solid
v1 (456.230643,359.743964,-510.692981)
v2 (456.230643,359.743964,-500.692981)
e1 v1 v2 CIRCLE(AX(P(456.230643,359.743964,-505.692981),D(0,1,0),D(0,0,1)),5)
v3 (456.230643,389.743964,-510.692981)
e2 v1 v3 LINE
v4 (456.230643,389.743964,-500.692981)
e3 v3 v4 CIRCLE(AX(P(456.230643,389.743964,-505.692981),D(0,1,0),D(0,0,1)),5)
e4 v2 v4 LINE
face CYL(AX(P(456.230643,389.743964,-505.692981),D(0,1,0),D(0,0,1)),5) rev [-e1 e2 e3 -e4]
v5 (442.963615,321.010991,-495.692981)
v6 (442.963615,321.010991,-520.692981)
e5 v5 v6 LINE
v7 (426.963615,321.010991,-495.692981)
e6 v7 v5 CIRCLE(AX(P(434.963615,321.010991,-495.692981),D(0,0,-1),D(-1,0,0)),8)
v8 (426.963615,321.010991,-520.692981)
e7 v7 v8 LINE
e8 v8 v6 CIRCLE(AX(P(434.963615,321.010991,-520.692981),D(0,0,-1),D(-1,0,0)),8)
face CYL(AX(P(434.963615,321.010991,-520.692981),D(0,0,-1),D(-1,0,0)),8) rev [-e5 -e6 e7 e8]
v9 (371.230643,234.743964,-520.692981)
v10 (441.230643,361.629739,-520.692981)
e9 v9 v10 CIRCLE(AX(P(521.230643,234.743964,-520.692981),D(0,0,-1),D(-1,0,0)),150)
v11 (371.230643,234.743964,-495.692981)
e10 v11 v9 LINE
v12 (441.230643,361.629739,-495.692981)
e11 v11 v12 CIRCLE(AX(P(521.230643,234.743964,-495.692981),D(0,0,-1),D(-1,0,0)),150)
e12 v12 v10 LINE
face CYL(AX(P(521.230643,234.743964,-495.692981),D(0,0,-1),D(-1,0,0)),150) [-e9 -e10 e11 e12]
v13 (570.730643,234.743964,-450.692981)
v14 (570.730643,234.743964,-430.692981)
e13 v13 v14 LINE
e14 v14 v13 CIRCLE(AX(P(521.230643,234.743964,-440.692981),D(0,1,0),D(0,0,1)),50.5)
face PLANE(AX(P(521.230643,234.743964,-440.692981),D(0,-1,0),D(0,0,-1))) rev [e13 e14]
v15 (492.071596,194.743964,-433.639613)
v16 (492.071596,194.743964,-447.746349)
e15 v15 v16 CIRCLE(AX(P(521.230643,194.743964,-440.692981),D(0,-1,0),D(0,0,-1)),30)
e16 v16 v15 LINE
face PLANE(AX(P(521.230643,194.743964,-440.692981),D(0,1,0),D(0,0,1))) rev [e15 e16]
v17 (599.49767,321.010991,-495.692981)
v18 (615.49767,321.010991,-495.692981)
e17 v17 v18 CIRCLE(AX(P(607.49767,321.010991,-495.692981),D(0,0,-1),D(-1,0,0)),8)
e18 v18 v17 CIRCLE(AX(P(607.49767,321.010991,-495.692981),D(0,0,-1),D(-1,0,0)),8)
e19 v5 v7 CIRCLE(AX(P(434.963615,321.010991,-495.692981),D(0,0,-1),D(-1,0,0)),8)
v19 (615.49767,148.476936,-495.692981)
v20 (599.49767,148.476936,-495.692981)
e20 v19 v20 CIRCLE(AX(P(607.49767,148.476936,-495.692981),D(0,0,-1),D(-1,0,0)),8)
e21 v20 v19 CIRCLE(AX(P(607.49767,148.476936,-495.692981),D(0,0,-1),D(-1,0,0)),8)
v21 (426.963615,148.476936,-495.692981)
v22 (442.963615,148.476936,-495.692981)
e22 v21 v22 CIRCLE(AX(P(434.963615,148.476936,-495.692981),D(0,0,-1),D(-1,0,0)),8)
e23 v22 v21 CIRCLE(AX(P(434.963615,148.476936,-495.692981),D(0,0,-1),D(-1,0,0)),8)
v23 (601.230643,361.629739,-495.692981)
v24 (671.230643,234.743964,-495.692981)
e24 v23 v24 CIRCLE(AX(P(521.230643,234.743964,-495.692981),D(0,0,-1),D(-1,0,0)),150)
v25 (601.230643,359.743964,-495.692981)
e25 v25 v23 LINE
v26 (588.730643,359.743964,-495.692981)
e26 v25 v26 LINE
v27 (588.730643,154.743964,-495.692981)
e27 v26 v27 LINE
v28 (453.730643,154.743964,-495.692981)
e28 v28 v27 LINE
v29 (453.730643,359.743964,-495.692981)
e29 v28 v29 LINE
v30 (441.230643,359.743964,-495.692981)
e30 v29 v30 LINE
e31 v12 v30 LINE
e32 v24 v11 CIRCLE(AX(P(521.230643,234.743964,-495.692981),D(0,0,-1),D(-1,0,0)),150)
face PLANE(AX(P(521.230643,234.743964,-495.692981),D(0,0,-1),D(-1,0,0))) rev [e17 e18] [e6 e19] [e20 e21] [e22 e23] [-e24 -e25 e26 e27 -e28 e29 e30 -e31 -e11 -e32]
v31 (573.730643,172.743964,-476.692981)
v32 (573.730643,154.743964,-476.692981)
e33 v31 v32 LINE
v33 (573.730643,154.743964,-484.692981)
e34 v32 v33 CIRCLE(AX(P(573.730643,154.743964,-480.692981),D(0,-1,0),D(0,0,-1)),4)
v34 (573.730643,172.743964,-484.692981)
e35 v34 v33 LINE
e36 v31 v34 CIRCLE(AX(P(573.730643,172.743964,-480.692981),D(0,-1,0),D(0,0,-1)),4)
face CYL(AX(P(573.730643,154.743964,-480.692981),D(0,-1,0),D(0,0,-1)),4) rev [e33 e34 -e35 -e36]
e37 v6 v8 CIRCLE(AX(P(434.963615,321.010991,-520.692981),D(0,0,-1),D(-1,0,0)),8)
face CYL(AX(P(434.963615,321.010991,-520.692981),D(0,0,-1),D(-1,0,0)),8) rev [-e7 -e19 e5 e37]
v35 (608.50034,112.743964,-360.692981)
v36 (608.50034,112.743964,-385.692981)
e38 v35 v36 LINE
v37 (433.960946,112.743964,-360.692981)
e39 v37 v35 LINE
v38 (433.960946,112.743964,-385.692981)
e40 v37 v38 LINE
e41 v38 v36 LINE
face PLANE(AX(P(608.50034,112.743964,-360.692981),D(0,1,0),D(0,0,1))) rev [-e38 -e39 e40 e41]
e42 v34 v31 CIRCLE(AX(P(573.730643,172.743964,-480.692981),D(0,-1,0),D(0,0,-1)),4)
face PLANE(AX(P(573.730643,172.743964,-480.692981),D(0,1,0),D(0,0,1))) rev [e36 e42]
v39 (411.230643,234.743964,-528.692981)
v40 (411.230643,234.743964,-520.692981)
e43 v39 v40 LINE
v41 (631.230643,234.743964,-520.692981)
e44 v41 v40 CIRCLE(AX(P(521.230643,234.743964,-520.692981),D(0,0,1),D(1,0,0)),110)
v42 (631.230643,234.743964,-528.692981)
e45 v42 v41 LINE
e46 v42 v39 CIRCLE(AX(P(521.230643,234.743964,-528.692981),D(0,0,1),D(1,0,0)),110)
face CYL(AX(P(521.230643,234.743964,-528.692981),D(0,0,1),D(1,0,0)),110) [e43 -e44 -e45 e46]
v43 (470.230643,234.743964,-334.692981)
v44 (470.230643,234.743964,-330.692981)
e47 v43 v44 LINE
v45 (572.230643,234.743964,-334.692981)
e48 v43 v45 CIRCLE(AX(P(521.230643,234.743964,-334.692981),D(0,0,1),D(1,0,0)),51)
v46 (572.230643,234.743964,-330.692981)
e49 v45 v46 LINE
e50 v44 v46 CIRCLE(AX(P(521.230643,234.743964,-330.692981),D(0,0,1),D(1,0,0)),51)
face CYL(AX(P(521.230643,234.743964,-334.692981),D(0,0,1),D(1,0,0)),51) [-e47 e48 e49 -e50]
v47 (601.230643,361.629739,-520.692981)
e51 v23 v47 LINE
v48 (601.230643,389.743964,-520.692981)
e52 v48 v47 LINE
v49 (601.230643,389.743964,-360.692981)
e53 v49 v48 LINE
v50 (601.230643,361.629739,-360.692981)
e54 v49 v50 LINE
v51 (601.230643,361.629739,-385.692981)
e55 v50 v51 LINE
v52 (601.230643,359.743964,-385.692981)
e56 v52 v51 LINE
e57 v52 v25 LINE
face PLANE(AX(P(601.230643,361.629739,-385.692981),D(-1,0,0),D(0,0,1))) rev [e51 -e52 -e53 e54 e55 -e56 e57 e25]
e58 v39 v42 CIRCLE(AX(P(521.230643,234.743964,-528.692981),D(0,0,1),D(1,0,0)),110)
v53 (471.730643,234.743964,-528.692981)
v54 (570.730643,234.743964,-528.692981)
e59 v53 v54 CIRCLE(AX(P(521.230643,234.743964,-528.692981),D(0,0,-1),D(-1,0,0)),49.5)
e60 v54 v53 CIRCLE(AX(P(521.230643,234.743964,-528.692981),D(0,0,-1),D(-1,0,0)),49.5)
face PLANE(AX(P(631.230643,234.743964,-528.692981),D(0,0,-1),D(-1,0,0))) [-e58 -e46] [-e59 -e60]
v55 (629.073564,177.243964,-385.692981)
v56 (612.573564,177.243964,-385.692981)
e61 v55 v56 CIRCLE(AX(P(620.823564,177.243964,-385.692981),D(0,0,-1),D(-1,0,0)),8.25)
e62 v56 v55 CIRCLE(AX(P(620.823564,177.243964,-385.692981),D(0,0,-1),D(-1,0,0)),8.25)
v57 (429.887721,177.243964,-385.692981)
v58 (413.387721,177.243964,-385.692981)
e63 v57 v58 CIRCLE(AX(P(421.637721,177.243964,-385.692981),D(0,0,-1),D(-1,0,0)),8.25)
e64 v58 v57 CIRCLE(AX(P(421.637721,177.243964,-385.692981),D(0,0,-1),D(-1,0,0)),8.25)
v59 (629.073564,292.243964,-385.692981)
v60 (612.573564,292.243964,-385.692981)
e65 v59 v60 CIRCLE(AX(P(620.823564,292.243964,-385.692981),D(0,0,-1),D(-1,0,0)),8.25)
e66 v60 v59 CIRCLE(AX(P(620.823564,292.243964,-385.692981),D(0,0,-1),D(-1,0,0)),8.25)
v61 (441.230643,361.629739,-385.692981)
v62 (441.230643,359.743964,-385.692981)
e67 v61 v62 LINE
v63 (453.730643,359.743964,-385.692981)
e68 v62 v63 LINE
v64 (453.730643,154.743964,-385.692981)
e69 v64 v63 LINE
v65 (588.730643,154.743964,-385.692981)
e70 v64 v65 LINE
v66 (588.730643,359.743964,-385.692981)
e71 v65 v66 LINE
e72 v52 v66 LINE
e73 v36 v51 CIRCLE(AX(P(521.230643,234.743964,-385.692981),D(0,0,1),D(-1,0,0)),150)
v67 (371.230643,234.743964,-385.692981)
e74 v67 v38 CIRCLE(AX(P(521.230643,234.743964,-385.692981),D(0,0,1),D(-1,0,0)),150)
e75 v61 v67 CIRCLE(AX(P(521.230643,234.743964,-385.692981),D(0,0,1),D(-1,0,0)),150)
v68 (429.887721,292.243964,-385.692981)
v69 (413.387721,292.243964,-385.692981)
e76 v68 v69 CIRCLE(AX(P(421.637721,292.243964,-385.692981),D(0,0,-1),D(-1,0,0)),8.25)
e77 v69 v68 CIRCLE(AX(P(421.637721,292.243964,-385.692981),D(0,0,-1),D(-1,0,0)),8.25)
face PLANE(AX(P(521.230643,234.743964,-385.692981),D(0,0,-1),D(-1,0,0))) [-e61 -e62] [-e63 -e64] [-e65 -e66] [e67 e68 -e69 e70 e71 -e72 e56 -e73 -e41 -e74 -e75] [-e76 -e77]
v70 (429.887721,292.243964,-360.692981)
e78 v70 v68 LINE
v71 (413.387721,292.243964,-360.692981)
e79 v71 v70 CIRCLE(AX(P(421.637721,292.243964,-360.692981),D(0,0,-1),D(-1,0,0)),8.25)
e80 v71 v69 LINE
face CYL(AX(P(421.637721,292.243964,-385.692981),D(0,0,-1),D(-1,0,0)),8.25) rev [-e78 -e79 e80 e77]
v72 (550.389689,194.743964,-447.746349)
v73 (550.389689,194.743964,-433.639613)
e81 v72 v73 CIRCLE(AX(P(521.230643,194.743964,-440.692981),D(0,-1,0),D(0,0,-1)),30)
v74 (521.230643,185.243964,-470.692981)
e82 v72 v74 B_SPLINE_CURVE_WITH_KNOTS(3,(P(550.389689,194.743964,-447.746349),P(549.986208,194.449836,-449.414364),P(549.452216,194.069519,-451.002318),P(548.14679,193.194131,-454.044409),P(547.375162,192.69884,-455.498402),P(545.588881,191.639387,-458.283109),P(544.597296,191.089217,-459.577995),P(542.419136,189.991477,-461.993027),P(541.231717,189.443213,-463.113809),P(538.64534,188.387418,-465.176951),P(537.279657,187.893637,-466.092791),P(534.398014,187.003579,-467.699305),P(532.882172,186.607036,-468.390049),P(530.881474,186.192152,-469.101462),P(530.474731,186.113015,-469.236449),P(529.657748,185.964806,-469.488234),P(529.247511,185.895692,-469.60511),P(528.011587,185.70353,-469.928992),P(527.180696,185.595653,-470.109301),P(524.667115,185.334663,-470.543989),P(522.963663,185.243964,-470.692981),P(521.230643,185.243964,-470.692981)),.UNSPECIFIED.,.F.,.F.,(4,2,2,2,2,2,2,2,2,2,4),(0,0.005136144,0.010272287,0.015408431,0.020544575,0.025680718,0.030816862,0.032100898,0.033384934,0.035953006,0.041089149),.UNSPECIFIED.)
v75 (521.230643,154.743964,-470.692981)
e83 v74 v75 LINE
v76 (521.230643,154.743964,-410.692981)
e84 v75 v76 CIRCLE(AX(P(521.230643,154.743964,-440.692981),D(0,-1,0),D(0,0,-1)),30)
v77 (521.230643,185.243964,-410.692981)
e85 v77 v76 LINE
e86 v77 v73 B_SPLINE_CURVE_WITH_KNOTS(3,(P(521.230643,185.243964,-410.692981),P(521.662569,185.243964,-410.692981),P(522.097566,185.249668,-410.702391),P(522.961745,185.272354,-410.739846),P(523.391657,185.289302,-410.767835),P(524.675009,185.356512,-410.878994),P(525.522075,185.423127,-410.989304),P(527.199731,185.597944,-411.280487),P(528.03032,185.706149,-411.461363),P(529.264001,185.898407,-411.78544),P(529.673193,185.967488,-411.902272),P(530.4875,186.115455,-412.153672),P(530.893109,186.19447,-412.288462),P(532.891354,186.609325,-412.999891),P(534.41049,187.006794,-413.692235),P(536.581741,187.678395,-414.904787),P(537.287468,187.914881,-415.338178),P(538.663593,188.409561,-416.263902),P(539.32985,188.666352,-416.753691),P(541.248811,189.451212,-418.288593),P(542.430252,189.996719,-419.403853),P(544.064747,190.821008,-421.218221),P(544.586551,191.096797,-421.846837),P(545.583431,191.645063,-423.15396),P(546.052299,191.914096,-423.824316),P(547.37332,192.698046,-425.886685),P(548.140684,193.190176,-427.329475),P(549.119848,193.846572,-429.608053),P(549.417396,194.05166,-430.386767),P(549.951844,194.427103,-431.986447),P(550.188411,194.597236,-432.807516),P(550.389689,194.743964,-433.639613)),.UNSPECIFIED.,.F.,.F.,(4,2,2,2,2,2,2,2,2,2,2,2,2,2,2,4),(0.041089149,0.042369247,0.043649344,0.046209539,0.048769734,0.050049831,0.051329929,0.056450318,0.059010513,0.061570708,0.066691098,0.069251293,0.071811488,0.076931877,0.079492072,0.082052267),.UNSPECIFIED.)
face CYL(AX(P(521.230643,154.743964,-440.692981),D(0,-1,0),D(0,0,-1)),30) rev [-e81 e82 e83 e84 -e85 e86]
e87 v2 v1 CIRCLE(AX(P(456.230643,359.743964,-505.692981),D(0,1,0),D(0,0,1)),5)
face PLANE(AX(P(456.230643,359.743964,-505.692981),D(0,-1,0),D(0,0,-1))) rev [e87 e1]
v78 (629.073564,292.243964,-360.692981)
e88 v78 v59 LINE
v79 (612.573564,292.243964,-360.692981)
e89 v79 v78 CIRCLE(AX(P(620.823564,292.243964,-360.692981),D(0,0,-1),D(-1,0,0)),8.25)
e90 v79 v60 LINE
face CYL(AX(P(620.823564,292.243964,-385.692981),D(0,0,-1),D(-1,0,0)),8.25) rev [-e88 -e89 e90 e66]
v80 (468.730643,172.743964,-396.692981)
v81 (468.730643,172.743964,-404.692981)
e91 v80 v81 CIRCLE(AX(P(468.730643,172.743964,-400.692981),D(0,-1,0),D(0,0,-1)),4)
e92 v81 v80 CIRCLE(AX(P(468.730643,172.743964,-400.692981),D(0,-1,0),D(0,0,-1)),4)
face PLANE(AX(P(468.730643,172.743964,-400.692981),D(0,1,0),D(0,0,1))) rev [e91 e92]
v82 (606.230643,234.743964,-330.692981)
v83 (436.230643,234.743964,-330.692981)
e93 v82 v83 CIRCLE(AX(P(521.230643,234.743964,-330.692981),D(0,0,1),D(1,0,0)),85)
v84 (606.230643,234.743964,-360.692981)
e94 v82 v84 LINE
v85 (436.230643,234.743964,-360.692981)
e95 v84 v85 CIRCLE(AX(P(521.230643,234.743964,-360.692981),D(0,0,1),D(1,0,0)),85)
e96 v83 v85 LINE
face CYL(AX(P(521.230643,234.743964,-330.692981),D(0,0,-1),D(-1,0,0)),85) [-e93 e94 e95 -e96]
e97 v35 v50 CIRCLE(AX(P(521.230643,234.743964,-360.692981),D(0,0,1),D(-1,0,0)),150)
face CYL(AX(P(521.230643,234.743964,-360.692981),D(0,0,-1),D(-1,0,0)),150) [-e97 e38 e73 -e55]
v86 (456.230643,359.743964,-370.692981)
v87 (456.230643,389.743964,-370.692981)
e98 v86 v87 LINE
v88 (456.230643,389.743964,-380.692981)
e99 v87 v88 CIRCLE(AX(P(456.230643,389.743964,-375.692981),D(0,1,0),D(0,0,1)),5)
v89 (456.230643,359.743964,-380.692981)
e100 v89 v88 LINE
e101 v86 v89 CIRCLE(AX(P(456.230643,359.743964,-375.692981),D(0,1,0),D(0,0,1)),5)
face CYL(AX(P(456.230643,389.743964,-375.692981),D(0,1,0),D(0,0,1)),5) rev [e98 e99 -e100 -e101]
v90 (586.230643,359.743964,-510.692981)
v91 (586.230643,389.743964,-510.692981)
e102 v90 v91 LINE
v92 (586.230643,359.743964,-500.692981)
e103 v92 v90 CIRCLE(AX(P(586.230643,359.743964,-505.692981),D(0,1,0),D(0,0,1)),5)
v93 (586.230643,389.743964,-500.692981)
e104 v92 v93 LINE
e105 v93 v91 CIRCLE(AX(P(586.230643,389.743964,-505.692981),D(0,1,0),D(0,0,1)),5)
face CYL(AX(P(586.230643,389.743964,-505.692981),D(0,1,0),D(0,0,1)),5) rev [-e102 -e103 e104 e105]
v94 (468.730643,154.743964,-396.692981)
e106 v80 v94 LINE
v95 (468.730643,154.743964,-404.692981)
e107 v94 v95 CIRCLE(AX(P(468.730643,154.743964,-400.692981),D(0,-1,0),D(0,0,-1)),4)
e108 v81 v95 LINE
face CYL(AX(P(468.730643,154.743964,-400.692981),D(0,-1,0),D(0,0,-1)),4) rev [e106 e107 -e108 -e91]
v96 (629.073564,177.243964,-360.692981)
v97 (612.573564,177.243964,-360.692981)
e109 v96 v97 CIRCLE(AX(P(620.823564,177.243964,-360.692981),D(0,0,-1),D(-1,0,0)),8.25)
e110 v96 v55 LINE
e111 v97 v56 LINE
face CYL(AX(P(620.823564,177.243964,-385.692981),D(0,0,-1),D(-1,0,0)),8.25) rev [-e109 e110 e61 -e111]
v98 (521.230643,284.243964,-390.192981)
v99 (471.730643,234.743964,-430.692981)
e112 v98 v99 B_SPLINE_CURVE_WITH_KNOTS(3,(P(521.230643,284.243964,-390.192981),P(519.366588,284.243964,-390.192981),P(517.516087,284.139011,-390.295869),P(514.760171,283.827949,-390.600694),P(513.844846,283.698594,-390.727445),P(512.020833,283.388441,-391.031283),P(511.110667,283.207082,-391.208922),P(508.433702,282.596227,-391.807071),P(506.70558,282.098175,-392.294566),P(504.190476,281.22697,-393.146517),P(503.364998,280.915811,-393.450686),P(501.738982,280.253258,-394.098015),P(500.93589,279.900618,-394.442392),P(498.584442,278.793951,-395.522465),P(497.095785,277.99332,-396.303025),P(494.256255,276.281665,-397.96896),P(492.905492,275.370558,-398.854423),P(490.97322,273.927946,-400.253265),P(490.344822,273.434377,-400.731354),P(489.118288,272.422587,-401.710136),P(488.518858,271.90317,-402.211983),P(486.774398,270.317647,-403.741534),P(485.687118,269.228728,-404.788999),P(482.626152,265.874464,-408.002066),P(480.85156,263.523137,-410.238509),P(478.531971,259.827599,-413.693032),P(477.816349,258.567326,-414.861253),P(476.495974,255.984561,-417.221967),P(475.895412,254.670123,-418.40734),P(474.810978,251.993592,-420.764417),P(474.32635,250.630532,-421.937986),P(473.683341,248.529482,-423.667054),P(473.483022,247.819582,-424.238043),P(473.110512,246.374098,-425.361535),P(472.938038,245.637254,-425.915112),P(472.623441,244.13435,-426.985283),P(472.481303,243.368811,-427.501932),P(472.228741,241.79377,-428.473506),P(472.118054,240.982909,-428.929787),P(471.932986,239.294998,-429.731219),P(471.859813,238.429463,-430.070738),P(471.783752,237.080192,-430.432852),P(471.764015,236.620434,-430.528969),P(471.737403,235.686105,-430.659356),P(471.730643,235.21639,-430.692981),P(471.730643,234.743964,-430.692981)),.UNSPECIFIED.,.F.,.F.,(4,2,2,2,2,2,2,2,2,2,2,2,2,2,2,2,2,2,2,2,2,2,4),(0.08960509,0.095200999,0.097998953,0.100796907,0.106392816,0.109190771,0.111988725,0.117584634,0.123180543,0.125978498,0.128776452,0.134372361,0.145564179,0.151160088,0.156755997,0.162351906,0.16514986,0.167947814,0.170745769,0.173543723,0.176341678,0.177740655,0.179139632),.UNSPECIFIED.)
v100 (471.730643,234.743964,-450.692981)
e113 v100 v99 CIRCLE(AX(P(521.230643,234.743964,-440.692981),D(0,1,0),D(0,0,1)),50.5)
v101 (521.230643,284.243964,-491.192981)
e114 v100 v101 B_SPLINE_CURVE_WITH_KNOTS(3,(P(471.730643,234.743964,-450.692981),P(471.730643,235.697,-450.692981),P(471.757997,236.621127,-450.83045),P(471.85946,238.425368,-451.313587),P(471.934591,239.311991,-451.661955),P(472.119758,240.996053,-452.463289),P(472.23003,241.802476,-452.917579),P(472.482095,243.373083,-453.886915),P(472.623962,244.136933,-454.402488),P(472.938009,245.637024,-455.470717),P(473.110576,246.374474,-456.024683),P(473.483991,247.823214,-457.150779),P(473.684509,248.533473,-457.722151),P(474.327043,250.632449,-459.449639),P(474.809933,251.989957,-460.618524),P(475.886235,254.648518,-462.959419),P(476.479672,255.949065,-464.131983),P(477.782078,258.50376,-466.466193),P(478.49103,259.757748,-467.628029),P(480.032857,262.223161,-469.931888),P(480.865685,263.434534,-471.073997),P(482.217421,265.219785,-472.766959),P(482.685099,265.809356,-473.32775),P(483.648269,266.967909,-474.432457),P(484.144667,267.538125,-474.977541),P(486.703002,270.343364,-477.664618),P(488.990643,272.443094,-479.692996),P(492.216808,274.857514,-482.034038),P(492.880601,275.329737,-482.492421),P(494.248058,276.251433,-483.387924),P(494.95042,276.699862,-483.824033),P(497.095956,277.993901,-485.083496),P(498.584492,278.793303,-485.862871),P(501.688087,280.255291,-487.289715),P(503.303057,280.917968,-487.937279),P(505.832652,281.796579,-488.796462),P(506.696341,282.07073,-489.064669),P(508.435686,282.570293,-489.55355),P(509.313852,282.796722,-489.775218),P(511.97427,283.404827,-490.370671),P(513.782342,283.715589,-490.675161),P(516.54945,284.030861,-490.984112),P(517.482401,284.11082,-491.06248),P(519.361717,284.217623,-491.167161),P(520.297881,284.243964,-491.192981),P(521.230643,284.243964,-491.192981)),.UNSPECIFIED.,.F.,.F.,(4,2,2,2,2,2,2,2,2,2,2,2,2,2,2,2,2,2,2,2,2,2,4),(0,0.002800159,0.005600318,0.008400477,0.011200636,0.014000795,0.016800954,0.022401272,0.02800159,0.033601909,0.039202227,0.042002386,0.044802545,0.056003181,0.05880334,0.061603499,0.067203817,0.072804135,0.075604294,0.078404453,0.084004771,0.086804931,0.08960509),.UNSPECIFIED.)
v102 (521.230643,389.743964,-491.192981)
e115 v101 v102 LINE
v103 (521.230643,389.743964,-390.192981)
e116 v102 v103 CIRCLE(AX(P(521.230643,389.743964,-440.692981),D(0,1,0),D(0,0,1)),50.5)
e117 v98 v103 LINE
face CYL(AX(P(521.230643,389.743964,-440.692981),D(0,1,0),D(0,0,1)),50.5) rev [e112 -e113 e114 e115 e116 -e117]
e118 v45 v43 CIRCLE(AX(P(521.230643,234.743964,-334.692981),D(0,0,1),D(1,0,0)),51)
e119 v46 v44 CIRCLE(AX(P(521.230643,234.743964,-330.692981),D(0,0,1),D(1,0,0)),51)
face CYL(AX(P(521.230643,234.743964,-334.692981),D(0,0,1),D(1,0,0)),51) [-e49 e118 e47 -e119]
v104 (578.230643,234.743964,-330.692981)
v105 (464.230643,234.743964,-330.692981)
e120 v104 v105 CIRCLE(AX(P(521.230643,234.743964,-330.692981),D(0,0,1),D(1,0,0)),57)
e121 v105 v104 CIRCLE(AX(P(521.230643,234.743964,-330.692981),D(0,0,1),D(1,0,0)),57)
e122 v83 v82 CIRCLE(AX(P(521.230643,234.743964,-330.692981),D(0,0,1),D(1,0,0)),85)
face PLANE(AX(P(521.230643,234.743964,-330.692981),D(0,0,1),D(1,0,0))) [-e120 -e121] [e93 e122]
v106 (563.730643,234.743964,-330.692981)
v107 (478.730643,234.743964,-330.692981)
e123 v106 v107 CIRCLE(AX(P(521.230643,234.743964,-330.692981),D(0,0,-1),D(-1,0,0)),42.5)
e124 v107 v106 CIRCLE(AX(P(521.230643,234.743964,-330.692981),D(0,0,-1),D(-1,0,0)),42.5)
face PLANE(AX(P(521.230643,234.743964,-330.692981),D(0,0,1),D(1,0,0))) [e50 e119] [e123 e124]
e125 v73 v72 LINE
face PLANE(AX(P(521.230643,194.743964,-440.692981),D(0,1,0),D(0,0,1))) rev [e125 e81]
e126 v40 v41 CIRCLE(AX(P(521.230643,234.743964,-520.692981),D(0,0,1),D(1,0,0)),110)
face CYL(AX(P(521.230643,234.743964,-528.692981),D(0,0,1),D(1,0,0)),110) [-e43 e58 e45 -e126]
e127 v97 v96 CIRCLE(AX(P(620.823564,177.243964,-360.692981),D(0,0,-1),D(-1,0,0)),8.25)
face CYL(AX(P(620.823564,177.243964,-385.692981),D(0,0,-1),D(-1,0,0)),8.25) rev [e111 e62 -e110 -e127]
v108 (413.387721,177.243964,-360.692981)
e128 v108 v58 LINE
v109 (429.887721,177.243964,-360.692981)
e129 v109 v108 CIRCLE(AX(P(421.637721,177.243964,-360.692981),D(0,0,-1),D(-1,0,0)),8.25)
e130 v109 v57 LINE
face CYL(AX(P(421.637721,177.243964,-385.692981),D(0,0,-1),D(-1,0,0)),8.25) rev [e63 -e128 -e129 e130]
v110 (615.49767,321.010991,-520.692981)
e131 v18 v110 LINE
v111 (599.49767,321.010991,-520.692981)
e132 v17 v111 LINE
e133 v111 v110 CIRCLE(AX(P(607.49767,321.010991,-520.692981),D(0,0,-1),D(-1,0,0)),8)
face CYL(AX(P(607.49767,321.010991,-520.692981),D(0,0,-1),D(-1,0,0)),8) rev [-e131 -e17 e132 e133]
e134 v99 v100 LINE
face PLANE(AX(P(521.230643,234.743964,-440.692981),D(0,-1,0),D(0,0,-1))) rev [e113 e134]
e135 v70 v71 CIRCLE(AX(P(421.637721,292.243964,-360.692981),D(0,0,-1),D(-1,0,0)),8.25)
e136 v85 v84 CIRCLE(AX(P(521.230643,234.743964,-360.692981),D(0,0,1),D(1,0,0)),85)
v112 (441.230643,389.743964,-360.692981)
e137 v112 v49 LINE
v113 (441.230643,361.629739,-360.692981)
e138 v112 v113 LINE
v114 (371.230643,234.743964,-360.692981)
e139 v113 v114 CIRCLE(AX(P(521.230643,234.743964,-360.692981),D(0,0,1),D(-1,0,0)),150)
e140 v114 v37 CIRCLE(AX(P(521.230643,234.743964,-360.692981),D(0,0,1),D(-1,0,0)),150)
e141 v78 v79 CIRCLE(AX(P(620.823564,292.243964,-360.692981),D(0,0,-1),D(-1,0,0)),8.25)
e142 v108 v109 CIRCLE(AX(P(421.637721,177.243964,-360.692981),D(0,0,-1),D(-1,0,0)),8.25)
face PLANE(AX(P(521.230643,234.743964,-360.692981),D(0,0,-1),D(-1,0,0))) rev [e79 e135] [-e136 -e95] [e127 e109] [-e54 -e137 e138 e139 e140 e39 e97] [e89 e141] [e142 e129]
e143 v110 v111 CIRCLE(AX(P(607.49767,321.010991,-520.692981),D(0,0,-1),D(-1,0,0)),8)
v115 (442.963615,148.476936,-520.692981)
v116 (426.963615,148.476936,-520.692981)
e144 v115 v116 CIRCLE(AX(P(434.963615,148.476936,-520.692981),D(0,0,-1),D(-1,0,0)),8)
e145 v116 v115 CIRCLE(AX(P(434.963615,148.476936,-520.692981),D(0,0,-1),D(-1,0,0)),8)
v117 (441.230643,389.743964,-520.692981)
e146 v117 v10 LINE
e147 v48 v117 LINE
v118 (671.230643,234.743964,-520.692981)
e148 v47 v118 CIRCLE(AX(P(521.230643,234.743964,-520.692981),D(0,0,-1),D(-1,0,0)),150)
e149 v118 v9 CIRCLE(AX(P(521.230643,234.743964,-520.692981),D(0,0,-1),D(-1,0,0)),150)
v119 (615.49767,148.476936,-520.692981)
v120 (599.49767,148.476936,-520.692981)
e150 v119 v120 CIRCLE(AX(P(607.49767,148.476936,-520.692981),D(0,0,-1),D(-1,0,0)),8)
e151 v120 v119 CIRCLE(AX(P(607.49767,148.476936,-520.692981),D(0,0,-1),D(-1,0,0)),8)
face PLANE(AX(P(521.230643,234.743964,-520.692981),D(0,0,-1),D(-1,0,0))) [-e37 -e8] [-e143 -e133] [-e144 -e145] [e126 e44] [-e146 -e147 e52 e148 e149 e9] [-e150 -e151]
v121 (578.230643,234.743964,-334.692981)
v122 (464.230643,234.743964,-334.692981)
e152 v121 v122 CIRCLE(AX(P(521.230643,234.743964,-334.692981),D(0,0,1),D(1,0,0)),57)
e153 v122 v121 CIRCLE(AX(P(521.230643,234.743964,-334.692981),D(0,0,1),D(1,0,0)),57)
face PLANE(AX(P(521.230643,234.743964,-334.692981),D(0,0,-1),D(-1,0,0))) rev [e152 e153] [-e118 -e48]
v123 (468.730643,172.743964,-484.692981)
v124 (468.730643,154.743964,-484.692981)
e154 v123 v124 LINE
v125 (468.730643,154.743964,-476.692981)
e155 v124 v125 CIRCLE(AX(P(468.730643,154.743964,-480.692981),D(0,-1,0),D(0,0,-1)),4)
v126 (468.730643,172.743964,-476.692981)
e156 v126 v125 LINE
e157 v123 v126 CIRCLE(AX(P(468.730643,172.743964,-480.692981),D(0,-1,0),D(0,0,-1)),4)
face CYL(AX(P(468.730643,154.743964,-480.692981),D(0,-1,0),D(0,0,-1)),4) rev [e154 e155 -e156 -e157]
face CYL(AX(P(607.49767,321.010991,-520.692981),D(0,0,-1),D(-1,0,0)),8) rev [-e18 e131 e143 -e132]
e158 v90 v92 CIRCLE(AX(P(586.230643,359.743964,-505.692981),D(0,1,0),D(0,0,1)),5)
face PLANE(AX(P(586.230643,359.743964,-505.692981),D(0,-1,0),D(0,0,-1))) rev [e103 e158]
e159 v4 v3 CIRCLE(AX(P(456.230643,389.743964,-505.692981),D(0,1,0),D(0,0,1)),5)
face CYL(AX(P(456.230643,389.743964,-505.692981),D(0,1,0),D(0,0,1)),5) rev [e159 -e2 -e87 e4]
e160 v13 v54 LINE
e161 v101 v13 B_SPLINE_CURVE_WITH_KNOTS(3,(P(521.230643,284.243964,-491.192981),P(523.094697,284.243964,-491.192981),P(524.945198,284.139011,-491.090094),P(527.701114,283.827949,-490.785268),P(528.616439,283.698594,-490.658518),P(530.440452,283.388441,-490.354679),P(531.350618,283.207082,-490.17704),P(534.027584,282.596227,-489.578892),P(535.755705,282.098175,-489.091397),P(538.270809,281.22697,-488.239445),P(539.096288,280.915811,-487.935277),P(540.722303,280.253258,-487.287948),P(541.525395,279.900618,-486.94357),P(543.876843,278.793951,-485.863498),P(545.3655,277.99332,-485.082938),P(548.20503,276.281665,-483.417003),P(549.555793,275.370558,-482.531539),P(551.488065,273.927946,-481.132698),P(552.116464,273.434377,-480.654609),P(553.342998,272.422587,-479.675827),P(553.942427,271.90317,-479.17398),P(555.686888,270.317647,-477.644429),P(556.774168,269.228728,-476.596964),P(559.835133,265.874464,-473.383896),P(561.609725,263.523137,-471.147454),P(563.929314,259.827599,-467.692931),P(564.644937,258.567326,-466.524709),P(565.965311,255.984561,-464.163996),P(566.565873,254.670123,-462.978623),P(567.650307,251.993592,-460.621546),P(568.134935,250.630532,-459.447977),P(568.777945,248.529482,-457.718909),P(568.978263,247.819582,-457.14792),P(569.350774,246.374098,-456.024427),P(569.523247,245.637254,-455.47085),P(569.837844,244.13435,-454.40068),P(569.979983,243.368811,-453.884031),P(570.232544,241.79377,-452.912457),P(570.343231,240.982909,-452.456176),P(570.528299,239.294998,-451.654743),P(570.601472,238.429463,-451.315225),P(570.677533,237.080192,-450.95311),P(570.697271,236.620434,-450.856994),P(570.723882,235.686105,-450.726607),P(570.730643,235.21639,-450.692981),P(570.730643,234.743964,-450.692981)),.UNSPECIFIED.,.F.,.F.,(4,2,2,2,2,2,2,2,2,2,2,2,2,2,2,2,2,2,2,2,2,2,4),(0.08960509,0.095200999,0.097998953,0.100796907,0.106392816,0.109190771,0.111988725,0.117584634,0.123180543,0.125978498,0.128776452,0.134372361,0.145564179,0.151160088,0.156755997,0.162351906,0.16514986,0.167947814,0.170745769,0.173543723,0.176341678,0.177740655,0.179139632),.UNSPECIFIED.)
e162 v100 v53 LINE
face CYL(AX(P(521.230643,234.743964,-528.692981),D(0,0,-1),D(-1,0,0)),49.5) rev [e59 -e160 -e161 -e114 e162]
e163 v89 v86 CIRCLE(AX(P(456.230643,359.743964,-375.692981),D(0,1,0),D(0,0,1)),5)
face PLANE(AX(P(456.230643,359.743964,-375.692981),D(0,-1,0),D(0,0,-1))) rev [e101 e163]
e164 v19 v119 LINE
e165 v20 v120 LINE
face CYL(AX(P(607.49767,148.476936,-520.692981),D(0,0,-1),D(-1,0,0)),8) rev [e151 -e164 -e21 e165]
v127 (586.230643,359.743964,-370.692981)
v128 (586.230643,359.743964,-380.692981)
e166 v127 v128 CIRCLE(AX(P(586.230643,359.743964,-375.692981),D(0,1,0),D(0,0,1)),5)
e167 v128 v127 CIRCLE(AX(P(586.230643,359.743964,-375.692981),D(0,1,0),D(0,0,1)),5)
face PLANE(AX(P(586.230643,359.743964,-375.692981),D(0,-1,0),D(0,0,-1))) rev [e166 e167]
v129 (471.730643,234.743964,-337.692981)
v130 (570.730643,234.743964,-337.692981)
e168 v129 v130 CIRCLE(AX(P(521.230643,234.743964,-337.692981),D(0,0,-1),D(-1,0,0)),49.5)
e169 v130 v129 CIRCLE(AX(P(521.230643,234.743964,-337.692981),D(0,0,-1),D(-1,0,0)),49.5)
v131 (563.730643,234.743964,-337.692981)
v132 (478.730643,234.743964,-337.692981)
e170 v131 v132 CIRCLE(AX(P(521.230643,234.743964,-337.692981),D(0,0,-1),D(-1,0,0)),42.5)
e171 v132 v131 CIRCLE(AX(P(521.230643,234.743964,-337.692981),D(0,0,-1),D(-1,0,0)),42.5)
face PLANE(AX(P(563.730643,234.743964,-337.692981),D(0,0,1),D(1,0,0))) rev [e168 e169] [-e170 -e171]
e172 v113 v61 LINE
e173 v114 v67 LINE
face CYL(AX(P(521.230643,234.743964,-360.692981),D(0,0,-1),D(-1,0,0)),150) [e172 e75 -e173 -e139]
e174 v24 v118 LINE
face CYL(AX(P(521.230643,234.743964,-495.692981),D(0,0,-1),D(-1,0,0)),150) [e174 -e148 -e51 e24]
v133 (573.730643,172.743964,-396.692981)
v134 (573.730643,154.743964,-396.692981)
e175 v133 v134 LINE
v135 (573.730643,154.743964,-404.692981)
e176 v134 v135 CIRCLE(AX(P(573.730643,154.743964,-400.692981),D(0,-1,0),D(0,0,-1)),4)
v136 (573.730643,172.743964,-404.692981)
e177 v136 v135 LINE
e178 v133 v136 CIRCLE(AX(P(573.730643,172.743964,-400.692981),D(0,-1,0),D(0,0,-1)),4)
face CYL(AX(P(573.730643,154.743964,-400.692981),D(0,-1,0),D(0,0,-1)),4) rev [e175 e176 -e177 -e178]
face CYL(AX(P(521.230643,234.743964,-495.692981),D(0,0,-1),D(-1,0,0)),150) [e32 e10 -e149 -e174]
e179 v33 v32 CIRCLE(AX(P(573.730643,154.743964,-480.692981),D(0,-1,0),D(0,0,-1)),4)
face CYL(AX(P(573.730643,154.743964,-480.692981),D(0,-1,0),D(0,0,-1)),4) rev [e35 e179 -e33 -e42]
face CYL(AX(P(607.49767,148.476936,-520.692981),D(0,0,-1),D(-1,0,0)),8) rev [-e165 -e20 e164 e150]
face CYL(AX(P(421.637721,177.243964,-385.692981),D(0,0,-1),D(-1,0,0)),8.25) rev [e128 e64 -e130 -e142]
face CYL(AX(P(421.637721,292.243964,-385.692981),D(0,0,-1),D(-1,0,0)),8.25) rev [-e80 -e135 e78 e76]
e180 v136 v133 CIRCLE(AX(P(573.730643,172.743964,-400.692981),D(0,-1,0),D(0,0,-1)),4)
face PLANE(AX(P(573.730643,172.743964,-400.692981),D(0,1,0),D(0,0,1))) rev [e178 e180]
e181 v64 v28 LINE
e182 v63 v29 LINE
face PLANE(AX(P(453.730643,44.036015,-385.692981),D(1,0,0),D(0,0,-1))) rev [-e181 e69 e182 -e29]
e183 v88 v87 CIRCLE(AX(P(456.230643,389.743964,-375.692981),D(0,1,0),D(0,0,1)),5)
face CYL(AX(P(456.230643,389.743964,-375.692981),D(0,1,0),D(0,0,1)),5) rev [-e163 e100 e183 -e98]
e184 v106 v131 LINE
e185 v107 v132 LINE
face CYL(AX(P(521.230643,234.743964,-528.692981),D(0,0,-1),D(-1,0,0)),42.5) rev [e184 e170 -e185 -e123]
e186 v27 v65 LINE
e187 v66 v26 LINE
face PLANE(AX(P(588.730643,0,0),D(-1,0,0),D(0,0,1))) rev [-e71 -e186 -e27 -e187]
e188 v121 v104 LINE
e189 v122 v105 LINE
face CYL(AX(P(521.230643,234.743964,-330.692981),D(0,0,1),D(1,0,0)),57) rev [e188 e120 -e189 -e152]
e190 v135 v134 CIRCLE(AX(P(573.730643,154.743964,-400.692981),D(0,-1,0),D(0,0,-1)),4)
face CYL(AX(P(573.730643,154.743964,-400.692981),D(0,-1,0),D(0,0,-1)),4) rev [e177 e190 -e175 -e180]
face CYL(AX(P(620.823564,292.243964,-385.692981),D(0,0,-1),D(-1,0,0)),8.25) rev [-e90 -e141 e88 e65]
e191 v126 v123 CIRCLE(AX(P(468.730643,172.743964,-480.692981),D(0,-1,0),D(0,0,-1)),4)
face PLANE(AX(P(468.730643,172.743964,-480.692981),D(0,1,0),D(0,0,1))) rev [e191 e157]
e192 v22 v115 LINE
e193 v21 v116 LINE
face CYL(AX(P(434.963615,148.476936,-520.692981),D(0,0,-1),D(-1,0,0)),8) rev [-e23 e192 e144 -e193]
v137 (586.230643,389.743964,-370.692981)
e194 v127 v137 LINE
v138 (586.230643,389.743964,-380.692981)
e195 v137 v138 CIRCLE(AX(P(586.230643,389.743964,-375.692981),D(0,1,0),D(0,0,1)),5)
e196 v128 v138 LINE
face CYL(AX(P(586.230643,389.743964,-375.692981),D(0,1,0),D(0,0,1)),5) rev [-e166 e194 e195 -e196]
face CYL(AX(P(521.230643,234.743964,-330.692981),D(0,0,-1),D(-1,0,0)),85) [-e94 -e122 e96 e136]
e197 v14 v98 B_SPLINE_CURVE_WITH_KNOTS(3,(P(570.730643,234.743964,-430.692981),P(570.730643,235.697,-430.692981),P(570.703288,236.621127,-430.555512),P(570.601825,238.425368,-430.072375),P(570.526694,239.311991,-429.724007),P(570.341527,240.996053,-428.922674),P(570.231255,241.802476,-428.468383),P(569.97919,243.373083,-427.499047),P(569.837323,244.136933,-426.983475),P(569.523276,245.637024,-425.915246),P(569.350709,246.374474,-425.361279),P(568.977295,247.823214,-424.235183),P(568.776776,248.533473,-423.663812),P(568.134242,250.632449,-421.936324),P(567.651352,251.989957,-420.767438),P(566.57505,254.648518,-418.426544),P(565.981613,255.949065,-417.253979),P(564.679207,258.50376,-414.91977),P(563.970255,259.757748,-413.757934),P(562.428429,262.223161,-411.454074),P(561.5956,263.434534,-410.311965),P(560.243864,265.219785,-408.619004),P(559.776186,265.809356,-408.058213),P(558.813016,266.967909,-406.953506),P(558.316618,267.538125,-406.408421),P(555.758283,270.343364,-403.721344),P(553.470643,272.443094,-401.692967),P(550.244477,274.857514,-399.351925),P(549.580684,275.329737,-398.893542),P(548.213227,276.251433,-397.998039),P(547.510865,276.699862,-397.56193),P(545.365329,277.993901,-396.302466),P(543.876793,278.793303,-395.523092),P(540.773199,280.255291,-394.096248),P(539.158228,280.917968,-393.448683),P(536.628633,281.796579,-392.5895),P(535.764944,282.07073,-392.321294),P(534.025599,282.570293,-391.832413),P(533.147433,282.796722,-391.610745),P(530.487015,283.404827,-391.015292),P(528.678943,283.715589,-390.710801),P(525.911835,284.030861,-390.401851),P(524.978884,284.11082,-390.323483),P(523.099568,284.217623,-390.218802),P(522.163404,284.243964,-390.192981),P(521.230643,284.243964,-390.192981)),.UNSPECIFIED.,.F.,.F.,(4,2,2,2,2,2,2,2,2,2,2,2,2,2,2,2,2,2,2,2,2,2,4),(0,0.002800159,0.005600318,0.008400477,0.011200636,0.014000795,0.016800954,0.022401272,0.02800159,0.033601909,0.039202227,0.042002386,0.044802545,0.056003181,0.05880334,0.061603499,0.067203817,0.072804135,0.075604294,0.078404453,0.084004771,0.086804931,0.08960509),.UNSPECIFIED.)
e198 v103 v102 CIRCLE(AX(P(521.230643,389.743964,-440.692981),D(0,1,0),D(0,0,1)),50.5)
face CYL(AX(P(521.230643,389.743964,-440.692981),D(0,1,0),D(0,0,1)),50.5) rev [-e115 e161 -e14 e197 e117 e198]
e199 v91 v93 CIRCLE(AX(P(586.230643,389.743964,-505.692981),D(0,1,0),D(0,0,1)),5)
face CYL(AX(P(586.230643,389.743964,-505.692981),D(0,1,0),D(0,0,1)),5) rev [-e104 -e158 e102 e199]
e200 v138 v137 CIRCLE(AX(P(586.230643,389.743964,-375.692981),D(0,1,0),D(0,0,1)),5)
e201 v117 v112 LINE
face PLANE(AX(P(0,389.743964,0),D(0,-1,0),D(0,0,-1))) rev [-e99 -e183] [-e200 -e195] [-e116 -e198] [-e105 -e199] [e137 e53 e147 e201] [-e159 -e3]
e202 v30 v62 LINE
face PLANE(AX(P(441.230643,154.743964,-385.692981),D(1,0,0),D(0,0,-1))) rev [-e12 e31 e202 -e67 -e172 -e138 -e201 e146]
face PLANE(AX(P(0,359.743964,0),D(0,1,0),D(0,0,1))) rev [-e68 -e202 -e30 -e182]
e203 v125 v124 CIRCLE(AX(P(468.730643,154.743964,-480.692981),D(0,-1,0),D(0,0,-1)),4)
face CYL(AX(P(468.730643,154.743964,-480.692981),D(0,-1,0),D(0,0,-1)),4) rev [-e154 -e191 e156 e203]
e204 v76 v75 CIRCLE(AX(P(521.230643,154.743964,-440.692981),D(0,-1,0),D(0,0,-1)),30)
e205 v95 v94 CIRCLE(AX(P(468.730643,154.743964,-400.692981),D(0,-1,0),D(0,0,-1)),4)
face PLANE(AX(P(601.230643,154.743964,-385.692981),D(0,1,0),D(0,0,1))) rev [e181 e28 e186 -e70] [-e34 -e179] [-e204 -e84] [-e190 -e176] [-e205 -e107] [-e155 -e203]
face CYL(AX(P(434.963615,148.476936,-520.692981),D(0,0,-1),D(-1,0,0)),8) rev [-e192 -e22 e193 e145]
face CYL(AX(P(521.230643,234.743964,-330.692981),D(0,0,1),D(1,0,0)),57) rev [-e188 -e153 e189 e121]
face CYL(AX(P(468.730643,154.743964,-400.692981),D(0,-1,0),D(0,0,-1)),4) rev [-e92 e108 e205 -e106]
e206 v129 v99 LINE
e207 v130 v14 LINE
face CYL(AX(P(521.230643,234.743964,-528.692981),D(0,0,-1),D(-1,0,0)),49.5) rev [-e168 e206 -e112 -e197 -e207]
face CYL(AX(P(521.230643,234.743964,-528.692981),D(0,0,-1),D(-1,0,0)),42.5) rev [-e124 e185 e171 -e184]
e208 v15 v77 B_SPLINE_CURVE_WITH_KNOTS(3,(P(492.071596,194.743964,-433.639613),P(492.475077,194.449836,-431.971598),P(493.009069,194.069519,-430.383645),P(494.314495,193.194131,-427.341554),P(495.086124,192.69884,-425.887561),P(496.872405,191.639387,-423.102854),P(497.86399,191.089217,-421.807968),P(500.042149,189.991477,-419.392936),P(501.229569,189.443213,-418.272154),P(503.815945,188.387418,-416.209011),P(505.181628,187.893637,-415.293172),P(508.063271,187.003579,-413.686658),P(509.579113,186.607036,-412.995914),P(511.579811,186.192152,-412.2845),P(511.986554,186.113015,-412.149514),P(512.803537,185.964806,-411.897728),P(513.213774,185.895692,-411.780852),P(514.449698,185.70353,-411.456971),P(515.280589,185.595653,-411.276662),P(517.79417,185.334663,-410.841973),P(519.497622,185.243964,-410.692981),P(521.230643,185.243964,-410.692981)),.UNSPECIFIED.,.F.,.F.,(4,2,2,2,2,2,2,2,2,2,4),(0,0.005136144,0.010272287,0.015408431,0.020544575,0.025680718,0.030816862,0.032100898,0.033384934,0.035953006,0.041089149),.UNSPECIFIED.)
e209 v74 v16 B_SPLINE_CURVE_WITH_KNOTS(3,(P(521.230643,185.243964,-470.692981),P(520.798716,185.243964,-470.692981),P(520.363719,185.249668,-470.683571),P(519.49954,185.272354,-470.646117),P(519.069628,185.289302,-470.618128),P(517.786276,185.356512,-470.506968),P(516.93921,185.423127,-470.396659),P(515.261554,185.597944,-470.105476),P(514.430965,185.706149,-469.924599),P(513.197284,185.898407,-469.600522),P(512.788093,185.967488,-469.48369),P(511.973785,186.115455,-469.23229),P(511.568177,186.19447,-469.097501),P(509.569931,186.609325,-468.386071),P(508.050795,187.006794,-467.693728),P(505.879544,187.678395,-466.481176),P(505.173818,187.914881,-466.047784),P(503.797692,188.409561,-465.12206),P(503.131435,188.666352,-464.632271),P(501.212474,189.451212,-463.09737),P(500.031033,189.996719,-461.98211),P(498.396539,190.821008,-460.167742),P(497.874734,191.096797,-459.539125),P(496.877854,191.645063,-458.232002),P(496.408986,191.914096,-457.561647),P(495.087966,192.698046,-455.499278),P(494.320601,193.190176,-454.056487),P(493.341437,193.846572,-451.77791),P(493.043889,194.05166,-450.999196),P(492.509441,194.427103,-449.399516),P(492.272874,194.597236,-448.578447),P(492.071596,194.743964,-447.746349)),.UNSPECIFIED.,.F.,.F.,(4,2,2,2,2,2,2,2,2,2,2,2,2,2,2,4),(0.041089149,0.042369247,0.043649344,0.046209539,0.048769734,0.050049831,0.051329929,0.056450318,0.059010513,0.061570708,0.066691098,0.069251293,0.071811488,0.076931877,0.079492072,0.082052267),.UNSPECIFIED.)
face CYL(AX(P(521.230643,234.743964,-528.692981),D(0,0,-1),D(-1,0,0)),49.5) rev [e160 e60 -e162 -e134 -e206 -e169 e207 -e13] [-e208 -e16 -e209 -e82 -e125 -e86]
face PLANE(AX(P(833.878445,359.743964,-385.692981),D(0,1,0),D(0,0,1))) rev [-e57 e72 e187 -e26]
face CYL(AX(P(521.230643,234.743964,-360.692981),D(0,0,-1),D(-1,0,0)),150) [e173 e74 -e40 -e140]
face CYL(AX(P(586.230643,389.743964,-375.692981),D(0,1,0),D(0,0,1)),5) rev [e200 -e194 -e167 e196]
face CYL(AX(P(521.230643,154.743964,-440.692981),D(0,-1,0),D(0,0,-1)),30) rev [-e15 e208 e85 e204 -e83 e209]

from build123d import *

# Parameters (mm, degrees)
BOSS_EXTRUDE1_DEPTH               = 25
SKETCH2_W                         = 160
SKETCH2_H                         = 206.885775404
BOSS_EXTRUDE2_DEPTH               = 110
BOSS_EXTRUDE3_DEPTH               = 25
SKETCH4_W                         = 160
SKETCH4_H                         = 160
BOSS_EXTRUDE4_DEPTH               = 28.114224596
CUT_EXTRUDE1_REACH                = 687.804
SKETCH6_W                         = 205
SKETCH6_H                         = 110
CUT_EXTRUDE2_REACH                = 894.915
SKETCH8_W                         = 12.5
SKETCH8_H                         = 110
SKETCH9_R                         = 85
BOSS_EXTRUDE5_DEPTH               = 30
HOLE1_D                           = 114
HOLE1_DEPTH                       = 4
SKETCH12_W                        = 110
SKETCH12_H                        = 8
SKETCH13_W                        = 51
SKETCH13_H                        = 4
F_16_0_16_DIAMETER_HOLE1_D        = 16
F_16_0_16_DIAMETER_HOLE1_DEPTH    = 25
F_16_5_16_5_DIAMETER_HOLE1_D      = 16.5
F_16_5_16_5_DIAMETER_HOLE1_DEPTH  = 55
F_10_0_10_DIAMETER_HOLE1_D        = 10
F_10_0_10_DIAMETER_HOLE1_DEPTH    = 30
F_8_0_8_DIAMETER_HOLE1_D          = 8
F_8_0_8_DIAMETER_HOLE1_DEPTH      = 18
M52_CLEARANCE_HOLE1_D             = 60
M52_CLEARANCE_HOLE1_DEPTH         = 40
M90_CLEARANCE_HOLE1_D             = 101
M90_CLEARANCE_HOLE1_DEPTH         = 155
M80_COUNTERBORE_HOLE1_D           = 85
M80_COUNTERBORE_HOLE1_CBORE_D     = 99
M80_COUNTERBORE_HOLE1_CBORE_DEPTH = 191


with BuildPart() as part:
    # Sketch1 → Boss-Extrude1 (new body)
    with BuildSketch(Plane(origin=(0, 0, -520.692981355), x_dir=(-1, 0, 0), z_dir=(0, 0, -1))):
        with BuildLine():
            Line((-441.230642584, 361.629739059), (-601.230642584, 361.629739059))
            ThreePointArc((-601.230642584, 361.629739059), (-521.230642584, 84.743963655), (-441.230642584, 361.629739059))
        make_face()
    extrude(amount=-BOSS_EXTRUDE1_DEPTH)

    # Sketch2 → Boss-Extrude2 (add)
    with BuildSketch(Plane.XY.offset(-495.692981355)):
        with Locations((521.230642584, 258.186851357)):
            Rectangle(SKETCH2_W, SKETCH2_H)
    extrude(amount=BOSS_EXTRUDE2_DEPTH)

    # Sketch3 → Boss-Extrude3 (add)
    with BuildSketch(Plane.XY.offset(-385.692981355)):
        with BuildLine():
            Line((608.500339501, 112.743963655), (433.960945667, 112.743963655))
            ThreePointArc((433.960945667, 112.743963655), (371.29458896, 239.123441208), (441.230642584, 361.629739059))
            Line((441.230642584, 361.629739059), (601.230642584, 361.629739059))
            ThreePointArc((601.230642584, 361.629739059), (671.166696208, 239.123441208), (608.500339501, 112.743963655))
        make_face()
    extrude(amount=BOSS_EXTRUDE3_DEPTH)

    # Sketch4 → Boss-Extrude4 (add)
    with BuildSketch(Plane(origin=(0, 361.629739059, 0), x_dir=(-1, 0, 0), z_dir=(0, 1, 0))):
        with Locations((-521.230642584, -440.692981355)):
            Rectangle(SKETCH4_W, SKETCH4_H)
    extrude(amount=BOSS_EXTRUDE4_DEPTH)

    # Sketch6 → Cut-Extrude1 (cut, up to next)
    with BuildSketch(Plane(origin=(588.730642584, 0, 0), x_dir=(0, -1, 0), z_dir=(-1, 0, 0)), mode=Mode.PRIVATE) as cut_extrude1_sk1:
        with Locations((-257.243963655, -440.692981355)):
            Rectangle(SKETCH6_W, SKETCH6_H)
    cut_extrude1_tool1 = extrude(cut_extrude1_sk1.sketch, amount=-CUT_EXTRUDE1_REACH, mode=Mode.PRIVATE) & part.part
    add(cut_extrude1_tool1.solids().sort_by_distance((588.730643, 257.243964, -440.692981))[0], mode=Mode.SUBTRACT)

    # Sketch8 → Cut-Extrude2 (cut, up to next)
    with BuildSketch(Plane(origin=(0, 359.743963655, 0), x_dir=(1, 0, 0), z_dir=(0, 1, 0)), mode=Mode.PRIVATE) as cut_extrude2_sk1:
        with Locations((447.480642584, 440.692981355)):
            Rectangle(SKETCH8_W, SKETCH8_H)
    cut_extrude2_tool1 = extrude(cut_extrude2_sk1.sketch, amount=-CUT_EXTRUDE2_REACH, mode=Mode.PRIVATE) & part.part
    add(cut_extrude2_tool1.solids().sort_by_distance((447.480643, 359.743964, -440.692981))[0], mode=Mode.SUBTRACT)

    # Sketch9 → Boss-Extrude5 (add)
    with BuildSketch(Plane.XY.offset(-360.692981355)):
        with Locations((521.230642584, 234.743963655)):
            Circle(SKETCH9_R)
    extrude(amount=BOSS_EXTRUDE5_DEPTH)

    # Hole1
    with Locations(Plane.XY.offset(-330.692981355)):
        with Locations((521.230642584, 234.743963655)):
            Hole(HOLE1_D / 2, depth=HOLE1_DEPTH)

    # Sketch12 → Revolve1 (revolve)
    with BuildSketch(Plane(origin=(0, 234.743963655, 0), x_dir=(1, 0, 0), z_dir=(0, 1, 0))):
        with Locations((576.230642584, 524.692981355)):
            Rectangle(SKETCH12_W, SKETCH12_H)
    revolve(axis=Axis((521.230642584, 234.743963655, -528.692981355), (0, 0, 1)))

    # Sketch13 → Revolve2 (revolve)
    with BuildSketch(Plane(origin=(0, 234.743963655, 0), x_dir=(1, 0, 0), z_dir=(0, 1, 0))):
        with Locations((546.730642584, 332.692981355)):
            Rectangle(SKETCH13_W, SKETCH13_H)
    revolve(axis=Axis((521.230642584, 234.743963655, -334.692981355), (0, 0, 1)))

    # Ø16.0 (16) diameter hole1
    with Locations(Plane(origin=(0, 0, -520.692981355), x_dir=(-1, 0, 0), z_dir=(0, 0, -1))):
        with Locations((-434.96361528, 321.010990959), (-607.497669889, 148.47693635), (-434.96361528, 148.47693635), (-607.497669889, 321.010990959)):
            Hole(F_16_0_16_DIAMETER_HOLE1_D / 2, depth=F_16_0_16_DIAMETER_HOLE1_DEPTH)

    # Ø16.5 (16.5) diameter hole1
    with Locations(Plane(origin=(0, 0, -385.692981355), x_dir=(-1, 0, 0), z_dir=(0, 0, -1))):
        with Locations((-620.82356402, 292.243963655), (-421.637721149, 177.243963655), (-421.637721149, 292.243963655), (-620.82356402, 177.243963655)):
            Hole(F_16_5_16_5_DIAMETER_HOLE1_D / 2, depth=F_16_5_16_5_DIAMETER_HOLE1_DEPTH)

    # Ø10.0 (10) diameter hole1
    with Locations(Plane(origin=(0, 389.743963655, 0), x_dir=(1, 0, 0), z_dir=(0, 1, 0))):
        with Locations((456.230642584, 505.692981355), (586.230642584, 505.692981355), (586.230642584, 375.692981355), (456.230642584, 375.692981355)):
            Hole(F_10_0_10_DIAMETER_HOLE1_D / 2, depth=F_10_0_10_DIAMETER_HOLE1_DEPTH)

    # Ø8.0 (8) diameter hole1
    with Locations(Plane(origin=(0, 154.743963655, 0), x_dir=(-1, 0, 0), z_dir=(0, -1, 0))):
        with Locations((-468.730642584, 480.692981355), (-573.730642584, 400.692981355), (-573.730642584, 480.692981355), (-468.730642584, 400.692981355)):
            Hole(F_8_0_8_DIAMETER_HOLE1_D / 2, depth=F_8_0_8_DIAMETER_HOLE1_DEPTH)

    # M52 clearance hole1
    with Locations(Plane(origin=(0, 154.743963655, 0), x_dir=(-1, 0, 0), z_dir=(0, -1, 0))):
        with Locations((-521.230642584, 440.692981355)):
            Hole(M52_CLEARANCE_HOLE1_D / 2, depth=M52_CLEARANCE_HOLE1_DEPTH)

    # M90 clearance hole1
    with Locations(Plane(origin=(0, 389.743963655, 0), x_dir=(1, 0, 0), z_dir=(0, 1, 0))):
        with Locations((521.230642584, 440.692981355)):
            Hole(M90_CLEARANCE_HOLE1_D / 2, depth=M90_CLEARANCE_HOLE1_DEPTH)

    # M80 counterbore hole1 (through all)
    with Locations(Plane(origin=(0, 0, -528.692981355), x_dir=(-1, 0, 0), z_dir=(0, 0, -1))):
        with Locations((-521.230642584, 234.743963655)):
            CounterBoreHole(M80_COUNTERBORE_HOLE1_D / 2, M80_COUNTERBORE_HOLE1_CBORE_D / 2, M80_COUNTERBORE_HOLE1_CBORE_DEPTH)


solid = part.part
